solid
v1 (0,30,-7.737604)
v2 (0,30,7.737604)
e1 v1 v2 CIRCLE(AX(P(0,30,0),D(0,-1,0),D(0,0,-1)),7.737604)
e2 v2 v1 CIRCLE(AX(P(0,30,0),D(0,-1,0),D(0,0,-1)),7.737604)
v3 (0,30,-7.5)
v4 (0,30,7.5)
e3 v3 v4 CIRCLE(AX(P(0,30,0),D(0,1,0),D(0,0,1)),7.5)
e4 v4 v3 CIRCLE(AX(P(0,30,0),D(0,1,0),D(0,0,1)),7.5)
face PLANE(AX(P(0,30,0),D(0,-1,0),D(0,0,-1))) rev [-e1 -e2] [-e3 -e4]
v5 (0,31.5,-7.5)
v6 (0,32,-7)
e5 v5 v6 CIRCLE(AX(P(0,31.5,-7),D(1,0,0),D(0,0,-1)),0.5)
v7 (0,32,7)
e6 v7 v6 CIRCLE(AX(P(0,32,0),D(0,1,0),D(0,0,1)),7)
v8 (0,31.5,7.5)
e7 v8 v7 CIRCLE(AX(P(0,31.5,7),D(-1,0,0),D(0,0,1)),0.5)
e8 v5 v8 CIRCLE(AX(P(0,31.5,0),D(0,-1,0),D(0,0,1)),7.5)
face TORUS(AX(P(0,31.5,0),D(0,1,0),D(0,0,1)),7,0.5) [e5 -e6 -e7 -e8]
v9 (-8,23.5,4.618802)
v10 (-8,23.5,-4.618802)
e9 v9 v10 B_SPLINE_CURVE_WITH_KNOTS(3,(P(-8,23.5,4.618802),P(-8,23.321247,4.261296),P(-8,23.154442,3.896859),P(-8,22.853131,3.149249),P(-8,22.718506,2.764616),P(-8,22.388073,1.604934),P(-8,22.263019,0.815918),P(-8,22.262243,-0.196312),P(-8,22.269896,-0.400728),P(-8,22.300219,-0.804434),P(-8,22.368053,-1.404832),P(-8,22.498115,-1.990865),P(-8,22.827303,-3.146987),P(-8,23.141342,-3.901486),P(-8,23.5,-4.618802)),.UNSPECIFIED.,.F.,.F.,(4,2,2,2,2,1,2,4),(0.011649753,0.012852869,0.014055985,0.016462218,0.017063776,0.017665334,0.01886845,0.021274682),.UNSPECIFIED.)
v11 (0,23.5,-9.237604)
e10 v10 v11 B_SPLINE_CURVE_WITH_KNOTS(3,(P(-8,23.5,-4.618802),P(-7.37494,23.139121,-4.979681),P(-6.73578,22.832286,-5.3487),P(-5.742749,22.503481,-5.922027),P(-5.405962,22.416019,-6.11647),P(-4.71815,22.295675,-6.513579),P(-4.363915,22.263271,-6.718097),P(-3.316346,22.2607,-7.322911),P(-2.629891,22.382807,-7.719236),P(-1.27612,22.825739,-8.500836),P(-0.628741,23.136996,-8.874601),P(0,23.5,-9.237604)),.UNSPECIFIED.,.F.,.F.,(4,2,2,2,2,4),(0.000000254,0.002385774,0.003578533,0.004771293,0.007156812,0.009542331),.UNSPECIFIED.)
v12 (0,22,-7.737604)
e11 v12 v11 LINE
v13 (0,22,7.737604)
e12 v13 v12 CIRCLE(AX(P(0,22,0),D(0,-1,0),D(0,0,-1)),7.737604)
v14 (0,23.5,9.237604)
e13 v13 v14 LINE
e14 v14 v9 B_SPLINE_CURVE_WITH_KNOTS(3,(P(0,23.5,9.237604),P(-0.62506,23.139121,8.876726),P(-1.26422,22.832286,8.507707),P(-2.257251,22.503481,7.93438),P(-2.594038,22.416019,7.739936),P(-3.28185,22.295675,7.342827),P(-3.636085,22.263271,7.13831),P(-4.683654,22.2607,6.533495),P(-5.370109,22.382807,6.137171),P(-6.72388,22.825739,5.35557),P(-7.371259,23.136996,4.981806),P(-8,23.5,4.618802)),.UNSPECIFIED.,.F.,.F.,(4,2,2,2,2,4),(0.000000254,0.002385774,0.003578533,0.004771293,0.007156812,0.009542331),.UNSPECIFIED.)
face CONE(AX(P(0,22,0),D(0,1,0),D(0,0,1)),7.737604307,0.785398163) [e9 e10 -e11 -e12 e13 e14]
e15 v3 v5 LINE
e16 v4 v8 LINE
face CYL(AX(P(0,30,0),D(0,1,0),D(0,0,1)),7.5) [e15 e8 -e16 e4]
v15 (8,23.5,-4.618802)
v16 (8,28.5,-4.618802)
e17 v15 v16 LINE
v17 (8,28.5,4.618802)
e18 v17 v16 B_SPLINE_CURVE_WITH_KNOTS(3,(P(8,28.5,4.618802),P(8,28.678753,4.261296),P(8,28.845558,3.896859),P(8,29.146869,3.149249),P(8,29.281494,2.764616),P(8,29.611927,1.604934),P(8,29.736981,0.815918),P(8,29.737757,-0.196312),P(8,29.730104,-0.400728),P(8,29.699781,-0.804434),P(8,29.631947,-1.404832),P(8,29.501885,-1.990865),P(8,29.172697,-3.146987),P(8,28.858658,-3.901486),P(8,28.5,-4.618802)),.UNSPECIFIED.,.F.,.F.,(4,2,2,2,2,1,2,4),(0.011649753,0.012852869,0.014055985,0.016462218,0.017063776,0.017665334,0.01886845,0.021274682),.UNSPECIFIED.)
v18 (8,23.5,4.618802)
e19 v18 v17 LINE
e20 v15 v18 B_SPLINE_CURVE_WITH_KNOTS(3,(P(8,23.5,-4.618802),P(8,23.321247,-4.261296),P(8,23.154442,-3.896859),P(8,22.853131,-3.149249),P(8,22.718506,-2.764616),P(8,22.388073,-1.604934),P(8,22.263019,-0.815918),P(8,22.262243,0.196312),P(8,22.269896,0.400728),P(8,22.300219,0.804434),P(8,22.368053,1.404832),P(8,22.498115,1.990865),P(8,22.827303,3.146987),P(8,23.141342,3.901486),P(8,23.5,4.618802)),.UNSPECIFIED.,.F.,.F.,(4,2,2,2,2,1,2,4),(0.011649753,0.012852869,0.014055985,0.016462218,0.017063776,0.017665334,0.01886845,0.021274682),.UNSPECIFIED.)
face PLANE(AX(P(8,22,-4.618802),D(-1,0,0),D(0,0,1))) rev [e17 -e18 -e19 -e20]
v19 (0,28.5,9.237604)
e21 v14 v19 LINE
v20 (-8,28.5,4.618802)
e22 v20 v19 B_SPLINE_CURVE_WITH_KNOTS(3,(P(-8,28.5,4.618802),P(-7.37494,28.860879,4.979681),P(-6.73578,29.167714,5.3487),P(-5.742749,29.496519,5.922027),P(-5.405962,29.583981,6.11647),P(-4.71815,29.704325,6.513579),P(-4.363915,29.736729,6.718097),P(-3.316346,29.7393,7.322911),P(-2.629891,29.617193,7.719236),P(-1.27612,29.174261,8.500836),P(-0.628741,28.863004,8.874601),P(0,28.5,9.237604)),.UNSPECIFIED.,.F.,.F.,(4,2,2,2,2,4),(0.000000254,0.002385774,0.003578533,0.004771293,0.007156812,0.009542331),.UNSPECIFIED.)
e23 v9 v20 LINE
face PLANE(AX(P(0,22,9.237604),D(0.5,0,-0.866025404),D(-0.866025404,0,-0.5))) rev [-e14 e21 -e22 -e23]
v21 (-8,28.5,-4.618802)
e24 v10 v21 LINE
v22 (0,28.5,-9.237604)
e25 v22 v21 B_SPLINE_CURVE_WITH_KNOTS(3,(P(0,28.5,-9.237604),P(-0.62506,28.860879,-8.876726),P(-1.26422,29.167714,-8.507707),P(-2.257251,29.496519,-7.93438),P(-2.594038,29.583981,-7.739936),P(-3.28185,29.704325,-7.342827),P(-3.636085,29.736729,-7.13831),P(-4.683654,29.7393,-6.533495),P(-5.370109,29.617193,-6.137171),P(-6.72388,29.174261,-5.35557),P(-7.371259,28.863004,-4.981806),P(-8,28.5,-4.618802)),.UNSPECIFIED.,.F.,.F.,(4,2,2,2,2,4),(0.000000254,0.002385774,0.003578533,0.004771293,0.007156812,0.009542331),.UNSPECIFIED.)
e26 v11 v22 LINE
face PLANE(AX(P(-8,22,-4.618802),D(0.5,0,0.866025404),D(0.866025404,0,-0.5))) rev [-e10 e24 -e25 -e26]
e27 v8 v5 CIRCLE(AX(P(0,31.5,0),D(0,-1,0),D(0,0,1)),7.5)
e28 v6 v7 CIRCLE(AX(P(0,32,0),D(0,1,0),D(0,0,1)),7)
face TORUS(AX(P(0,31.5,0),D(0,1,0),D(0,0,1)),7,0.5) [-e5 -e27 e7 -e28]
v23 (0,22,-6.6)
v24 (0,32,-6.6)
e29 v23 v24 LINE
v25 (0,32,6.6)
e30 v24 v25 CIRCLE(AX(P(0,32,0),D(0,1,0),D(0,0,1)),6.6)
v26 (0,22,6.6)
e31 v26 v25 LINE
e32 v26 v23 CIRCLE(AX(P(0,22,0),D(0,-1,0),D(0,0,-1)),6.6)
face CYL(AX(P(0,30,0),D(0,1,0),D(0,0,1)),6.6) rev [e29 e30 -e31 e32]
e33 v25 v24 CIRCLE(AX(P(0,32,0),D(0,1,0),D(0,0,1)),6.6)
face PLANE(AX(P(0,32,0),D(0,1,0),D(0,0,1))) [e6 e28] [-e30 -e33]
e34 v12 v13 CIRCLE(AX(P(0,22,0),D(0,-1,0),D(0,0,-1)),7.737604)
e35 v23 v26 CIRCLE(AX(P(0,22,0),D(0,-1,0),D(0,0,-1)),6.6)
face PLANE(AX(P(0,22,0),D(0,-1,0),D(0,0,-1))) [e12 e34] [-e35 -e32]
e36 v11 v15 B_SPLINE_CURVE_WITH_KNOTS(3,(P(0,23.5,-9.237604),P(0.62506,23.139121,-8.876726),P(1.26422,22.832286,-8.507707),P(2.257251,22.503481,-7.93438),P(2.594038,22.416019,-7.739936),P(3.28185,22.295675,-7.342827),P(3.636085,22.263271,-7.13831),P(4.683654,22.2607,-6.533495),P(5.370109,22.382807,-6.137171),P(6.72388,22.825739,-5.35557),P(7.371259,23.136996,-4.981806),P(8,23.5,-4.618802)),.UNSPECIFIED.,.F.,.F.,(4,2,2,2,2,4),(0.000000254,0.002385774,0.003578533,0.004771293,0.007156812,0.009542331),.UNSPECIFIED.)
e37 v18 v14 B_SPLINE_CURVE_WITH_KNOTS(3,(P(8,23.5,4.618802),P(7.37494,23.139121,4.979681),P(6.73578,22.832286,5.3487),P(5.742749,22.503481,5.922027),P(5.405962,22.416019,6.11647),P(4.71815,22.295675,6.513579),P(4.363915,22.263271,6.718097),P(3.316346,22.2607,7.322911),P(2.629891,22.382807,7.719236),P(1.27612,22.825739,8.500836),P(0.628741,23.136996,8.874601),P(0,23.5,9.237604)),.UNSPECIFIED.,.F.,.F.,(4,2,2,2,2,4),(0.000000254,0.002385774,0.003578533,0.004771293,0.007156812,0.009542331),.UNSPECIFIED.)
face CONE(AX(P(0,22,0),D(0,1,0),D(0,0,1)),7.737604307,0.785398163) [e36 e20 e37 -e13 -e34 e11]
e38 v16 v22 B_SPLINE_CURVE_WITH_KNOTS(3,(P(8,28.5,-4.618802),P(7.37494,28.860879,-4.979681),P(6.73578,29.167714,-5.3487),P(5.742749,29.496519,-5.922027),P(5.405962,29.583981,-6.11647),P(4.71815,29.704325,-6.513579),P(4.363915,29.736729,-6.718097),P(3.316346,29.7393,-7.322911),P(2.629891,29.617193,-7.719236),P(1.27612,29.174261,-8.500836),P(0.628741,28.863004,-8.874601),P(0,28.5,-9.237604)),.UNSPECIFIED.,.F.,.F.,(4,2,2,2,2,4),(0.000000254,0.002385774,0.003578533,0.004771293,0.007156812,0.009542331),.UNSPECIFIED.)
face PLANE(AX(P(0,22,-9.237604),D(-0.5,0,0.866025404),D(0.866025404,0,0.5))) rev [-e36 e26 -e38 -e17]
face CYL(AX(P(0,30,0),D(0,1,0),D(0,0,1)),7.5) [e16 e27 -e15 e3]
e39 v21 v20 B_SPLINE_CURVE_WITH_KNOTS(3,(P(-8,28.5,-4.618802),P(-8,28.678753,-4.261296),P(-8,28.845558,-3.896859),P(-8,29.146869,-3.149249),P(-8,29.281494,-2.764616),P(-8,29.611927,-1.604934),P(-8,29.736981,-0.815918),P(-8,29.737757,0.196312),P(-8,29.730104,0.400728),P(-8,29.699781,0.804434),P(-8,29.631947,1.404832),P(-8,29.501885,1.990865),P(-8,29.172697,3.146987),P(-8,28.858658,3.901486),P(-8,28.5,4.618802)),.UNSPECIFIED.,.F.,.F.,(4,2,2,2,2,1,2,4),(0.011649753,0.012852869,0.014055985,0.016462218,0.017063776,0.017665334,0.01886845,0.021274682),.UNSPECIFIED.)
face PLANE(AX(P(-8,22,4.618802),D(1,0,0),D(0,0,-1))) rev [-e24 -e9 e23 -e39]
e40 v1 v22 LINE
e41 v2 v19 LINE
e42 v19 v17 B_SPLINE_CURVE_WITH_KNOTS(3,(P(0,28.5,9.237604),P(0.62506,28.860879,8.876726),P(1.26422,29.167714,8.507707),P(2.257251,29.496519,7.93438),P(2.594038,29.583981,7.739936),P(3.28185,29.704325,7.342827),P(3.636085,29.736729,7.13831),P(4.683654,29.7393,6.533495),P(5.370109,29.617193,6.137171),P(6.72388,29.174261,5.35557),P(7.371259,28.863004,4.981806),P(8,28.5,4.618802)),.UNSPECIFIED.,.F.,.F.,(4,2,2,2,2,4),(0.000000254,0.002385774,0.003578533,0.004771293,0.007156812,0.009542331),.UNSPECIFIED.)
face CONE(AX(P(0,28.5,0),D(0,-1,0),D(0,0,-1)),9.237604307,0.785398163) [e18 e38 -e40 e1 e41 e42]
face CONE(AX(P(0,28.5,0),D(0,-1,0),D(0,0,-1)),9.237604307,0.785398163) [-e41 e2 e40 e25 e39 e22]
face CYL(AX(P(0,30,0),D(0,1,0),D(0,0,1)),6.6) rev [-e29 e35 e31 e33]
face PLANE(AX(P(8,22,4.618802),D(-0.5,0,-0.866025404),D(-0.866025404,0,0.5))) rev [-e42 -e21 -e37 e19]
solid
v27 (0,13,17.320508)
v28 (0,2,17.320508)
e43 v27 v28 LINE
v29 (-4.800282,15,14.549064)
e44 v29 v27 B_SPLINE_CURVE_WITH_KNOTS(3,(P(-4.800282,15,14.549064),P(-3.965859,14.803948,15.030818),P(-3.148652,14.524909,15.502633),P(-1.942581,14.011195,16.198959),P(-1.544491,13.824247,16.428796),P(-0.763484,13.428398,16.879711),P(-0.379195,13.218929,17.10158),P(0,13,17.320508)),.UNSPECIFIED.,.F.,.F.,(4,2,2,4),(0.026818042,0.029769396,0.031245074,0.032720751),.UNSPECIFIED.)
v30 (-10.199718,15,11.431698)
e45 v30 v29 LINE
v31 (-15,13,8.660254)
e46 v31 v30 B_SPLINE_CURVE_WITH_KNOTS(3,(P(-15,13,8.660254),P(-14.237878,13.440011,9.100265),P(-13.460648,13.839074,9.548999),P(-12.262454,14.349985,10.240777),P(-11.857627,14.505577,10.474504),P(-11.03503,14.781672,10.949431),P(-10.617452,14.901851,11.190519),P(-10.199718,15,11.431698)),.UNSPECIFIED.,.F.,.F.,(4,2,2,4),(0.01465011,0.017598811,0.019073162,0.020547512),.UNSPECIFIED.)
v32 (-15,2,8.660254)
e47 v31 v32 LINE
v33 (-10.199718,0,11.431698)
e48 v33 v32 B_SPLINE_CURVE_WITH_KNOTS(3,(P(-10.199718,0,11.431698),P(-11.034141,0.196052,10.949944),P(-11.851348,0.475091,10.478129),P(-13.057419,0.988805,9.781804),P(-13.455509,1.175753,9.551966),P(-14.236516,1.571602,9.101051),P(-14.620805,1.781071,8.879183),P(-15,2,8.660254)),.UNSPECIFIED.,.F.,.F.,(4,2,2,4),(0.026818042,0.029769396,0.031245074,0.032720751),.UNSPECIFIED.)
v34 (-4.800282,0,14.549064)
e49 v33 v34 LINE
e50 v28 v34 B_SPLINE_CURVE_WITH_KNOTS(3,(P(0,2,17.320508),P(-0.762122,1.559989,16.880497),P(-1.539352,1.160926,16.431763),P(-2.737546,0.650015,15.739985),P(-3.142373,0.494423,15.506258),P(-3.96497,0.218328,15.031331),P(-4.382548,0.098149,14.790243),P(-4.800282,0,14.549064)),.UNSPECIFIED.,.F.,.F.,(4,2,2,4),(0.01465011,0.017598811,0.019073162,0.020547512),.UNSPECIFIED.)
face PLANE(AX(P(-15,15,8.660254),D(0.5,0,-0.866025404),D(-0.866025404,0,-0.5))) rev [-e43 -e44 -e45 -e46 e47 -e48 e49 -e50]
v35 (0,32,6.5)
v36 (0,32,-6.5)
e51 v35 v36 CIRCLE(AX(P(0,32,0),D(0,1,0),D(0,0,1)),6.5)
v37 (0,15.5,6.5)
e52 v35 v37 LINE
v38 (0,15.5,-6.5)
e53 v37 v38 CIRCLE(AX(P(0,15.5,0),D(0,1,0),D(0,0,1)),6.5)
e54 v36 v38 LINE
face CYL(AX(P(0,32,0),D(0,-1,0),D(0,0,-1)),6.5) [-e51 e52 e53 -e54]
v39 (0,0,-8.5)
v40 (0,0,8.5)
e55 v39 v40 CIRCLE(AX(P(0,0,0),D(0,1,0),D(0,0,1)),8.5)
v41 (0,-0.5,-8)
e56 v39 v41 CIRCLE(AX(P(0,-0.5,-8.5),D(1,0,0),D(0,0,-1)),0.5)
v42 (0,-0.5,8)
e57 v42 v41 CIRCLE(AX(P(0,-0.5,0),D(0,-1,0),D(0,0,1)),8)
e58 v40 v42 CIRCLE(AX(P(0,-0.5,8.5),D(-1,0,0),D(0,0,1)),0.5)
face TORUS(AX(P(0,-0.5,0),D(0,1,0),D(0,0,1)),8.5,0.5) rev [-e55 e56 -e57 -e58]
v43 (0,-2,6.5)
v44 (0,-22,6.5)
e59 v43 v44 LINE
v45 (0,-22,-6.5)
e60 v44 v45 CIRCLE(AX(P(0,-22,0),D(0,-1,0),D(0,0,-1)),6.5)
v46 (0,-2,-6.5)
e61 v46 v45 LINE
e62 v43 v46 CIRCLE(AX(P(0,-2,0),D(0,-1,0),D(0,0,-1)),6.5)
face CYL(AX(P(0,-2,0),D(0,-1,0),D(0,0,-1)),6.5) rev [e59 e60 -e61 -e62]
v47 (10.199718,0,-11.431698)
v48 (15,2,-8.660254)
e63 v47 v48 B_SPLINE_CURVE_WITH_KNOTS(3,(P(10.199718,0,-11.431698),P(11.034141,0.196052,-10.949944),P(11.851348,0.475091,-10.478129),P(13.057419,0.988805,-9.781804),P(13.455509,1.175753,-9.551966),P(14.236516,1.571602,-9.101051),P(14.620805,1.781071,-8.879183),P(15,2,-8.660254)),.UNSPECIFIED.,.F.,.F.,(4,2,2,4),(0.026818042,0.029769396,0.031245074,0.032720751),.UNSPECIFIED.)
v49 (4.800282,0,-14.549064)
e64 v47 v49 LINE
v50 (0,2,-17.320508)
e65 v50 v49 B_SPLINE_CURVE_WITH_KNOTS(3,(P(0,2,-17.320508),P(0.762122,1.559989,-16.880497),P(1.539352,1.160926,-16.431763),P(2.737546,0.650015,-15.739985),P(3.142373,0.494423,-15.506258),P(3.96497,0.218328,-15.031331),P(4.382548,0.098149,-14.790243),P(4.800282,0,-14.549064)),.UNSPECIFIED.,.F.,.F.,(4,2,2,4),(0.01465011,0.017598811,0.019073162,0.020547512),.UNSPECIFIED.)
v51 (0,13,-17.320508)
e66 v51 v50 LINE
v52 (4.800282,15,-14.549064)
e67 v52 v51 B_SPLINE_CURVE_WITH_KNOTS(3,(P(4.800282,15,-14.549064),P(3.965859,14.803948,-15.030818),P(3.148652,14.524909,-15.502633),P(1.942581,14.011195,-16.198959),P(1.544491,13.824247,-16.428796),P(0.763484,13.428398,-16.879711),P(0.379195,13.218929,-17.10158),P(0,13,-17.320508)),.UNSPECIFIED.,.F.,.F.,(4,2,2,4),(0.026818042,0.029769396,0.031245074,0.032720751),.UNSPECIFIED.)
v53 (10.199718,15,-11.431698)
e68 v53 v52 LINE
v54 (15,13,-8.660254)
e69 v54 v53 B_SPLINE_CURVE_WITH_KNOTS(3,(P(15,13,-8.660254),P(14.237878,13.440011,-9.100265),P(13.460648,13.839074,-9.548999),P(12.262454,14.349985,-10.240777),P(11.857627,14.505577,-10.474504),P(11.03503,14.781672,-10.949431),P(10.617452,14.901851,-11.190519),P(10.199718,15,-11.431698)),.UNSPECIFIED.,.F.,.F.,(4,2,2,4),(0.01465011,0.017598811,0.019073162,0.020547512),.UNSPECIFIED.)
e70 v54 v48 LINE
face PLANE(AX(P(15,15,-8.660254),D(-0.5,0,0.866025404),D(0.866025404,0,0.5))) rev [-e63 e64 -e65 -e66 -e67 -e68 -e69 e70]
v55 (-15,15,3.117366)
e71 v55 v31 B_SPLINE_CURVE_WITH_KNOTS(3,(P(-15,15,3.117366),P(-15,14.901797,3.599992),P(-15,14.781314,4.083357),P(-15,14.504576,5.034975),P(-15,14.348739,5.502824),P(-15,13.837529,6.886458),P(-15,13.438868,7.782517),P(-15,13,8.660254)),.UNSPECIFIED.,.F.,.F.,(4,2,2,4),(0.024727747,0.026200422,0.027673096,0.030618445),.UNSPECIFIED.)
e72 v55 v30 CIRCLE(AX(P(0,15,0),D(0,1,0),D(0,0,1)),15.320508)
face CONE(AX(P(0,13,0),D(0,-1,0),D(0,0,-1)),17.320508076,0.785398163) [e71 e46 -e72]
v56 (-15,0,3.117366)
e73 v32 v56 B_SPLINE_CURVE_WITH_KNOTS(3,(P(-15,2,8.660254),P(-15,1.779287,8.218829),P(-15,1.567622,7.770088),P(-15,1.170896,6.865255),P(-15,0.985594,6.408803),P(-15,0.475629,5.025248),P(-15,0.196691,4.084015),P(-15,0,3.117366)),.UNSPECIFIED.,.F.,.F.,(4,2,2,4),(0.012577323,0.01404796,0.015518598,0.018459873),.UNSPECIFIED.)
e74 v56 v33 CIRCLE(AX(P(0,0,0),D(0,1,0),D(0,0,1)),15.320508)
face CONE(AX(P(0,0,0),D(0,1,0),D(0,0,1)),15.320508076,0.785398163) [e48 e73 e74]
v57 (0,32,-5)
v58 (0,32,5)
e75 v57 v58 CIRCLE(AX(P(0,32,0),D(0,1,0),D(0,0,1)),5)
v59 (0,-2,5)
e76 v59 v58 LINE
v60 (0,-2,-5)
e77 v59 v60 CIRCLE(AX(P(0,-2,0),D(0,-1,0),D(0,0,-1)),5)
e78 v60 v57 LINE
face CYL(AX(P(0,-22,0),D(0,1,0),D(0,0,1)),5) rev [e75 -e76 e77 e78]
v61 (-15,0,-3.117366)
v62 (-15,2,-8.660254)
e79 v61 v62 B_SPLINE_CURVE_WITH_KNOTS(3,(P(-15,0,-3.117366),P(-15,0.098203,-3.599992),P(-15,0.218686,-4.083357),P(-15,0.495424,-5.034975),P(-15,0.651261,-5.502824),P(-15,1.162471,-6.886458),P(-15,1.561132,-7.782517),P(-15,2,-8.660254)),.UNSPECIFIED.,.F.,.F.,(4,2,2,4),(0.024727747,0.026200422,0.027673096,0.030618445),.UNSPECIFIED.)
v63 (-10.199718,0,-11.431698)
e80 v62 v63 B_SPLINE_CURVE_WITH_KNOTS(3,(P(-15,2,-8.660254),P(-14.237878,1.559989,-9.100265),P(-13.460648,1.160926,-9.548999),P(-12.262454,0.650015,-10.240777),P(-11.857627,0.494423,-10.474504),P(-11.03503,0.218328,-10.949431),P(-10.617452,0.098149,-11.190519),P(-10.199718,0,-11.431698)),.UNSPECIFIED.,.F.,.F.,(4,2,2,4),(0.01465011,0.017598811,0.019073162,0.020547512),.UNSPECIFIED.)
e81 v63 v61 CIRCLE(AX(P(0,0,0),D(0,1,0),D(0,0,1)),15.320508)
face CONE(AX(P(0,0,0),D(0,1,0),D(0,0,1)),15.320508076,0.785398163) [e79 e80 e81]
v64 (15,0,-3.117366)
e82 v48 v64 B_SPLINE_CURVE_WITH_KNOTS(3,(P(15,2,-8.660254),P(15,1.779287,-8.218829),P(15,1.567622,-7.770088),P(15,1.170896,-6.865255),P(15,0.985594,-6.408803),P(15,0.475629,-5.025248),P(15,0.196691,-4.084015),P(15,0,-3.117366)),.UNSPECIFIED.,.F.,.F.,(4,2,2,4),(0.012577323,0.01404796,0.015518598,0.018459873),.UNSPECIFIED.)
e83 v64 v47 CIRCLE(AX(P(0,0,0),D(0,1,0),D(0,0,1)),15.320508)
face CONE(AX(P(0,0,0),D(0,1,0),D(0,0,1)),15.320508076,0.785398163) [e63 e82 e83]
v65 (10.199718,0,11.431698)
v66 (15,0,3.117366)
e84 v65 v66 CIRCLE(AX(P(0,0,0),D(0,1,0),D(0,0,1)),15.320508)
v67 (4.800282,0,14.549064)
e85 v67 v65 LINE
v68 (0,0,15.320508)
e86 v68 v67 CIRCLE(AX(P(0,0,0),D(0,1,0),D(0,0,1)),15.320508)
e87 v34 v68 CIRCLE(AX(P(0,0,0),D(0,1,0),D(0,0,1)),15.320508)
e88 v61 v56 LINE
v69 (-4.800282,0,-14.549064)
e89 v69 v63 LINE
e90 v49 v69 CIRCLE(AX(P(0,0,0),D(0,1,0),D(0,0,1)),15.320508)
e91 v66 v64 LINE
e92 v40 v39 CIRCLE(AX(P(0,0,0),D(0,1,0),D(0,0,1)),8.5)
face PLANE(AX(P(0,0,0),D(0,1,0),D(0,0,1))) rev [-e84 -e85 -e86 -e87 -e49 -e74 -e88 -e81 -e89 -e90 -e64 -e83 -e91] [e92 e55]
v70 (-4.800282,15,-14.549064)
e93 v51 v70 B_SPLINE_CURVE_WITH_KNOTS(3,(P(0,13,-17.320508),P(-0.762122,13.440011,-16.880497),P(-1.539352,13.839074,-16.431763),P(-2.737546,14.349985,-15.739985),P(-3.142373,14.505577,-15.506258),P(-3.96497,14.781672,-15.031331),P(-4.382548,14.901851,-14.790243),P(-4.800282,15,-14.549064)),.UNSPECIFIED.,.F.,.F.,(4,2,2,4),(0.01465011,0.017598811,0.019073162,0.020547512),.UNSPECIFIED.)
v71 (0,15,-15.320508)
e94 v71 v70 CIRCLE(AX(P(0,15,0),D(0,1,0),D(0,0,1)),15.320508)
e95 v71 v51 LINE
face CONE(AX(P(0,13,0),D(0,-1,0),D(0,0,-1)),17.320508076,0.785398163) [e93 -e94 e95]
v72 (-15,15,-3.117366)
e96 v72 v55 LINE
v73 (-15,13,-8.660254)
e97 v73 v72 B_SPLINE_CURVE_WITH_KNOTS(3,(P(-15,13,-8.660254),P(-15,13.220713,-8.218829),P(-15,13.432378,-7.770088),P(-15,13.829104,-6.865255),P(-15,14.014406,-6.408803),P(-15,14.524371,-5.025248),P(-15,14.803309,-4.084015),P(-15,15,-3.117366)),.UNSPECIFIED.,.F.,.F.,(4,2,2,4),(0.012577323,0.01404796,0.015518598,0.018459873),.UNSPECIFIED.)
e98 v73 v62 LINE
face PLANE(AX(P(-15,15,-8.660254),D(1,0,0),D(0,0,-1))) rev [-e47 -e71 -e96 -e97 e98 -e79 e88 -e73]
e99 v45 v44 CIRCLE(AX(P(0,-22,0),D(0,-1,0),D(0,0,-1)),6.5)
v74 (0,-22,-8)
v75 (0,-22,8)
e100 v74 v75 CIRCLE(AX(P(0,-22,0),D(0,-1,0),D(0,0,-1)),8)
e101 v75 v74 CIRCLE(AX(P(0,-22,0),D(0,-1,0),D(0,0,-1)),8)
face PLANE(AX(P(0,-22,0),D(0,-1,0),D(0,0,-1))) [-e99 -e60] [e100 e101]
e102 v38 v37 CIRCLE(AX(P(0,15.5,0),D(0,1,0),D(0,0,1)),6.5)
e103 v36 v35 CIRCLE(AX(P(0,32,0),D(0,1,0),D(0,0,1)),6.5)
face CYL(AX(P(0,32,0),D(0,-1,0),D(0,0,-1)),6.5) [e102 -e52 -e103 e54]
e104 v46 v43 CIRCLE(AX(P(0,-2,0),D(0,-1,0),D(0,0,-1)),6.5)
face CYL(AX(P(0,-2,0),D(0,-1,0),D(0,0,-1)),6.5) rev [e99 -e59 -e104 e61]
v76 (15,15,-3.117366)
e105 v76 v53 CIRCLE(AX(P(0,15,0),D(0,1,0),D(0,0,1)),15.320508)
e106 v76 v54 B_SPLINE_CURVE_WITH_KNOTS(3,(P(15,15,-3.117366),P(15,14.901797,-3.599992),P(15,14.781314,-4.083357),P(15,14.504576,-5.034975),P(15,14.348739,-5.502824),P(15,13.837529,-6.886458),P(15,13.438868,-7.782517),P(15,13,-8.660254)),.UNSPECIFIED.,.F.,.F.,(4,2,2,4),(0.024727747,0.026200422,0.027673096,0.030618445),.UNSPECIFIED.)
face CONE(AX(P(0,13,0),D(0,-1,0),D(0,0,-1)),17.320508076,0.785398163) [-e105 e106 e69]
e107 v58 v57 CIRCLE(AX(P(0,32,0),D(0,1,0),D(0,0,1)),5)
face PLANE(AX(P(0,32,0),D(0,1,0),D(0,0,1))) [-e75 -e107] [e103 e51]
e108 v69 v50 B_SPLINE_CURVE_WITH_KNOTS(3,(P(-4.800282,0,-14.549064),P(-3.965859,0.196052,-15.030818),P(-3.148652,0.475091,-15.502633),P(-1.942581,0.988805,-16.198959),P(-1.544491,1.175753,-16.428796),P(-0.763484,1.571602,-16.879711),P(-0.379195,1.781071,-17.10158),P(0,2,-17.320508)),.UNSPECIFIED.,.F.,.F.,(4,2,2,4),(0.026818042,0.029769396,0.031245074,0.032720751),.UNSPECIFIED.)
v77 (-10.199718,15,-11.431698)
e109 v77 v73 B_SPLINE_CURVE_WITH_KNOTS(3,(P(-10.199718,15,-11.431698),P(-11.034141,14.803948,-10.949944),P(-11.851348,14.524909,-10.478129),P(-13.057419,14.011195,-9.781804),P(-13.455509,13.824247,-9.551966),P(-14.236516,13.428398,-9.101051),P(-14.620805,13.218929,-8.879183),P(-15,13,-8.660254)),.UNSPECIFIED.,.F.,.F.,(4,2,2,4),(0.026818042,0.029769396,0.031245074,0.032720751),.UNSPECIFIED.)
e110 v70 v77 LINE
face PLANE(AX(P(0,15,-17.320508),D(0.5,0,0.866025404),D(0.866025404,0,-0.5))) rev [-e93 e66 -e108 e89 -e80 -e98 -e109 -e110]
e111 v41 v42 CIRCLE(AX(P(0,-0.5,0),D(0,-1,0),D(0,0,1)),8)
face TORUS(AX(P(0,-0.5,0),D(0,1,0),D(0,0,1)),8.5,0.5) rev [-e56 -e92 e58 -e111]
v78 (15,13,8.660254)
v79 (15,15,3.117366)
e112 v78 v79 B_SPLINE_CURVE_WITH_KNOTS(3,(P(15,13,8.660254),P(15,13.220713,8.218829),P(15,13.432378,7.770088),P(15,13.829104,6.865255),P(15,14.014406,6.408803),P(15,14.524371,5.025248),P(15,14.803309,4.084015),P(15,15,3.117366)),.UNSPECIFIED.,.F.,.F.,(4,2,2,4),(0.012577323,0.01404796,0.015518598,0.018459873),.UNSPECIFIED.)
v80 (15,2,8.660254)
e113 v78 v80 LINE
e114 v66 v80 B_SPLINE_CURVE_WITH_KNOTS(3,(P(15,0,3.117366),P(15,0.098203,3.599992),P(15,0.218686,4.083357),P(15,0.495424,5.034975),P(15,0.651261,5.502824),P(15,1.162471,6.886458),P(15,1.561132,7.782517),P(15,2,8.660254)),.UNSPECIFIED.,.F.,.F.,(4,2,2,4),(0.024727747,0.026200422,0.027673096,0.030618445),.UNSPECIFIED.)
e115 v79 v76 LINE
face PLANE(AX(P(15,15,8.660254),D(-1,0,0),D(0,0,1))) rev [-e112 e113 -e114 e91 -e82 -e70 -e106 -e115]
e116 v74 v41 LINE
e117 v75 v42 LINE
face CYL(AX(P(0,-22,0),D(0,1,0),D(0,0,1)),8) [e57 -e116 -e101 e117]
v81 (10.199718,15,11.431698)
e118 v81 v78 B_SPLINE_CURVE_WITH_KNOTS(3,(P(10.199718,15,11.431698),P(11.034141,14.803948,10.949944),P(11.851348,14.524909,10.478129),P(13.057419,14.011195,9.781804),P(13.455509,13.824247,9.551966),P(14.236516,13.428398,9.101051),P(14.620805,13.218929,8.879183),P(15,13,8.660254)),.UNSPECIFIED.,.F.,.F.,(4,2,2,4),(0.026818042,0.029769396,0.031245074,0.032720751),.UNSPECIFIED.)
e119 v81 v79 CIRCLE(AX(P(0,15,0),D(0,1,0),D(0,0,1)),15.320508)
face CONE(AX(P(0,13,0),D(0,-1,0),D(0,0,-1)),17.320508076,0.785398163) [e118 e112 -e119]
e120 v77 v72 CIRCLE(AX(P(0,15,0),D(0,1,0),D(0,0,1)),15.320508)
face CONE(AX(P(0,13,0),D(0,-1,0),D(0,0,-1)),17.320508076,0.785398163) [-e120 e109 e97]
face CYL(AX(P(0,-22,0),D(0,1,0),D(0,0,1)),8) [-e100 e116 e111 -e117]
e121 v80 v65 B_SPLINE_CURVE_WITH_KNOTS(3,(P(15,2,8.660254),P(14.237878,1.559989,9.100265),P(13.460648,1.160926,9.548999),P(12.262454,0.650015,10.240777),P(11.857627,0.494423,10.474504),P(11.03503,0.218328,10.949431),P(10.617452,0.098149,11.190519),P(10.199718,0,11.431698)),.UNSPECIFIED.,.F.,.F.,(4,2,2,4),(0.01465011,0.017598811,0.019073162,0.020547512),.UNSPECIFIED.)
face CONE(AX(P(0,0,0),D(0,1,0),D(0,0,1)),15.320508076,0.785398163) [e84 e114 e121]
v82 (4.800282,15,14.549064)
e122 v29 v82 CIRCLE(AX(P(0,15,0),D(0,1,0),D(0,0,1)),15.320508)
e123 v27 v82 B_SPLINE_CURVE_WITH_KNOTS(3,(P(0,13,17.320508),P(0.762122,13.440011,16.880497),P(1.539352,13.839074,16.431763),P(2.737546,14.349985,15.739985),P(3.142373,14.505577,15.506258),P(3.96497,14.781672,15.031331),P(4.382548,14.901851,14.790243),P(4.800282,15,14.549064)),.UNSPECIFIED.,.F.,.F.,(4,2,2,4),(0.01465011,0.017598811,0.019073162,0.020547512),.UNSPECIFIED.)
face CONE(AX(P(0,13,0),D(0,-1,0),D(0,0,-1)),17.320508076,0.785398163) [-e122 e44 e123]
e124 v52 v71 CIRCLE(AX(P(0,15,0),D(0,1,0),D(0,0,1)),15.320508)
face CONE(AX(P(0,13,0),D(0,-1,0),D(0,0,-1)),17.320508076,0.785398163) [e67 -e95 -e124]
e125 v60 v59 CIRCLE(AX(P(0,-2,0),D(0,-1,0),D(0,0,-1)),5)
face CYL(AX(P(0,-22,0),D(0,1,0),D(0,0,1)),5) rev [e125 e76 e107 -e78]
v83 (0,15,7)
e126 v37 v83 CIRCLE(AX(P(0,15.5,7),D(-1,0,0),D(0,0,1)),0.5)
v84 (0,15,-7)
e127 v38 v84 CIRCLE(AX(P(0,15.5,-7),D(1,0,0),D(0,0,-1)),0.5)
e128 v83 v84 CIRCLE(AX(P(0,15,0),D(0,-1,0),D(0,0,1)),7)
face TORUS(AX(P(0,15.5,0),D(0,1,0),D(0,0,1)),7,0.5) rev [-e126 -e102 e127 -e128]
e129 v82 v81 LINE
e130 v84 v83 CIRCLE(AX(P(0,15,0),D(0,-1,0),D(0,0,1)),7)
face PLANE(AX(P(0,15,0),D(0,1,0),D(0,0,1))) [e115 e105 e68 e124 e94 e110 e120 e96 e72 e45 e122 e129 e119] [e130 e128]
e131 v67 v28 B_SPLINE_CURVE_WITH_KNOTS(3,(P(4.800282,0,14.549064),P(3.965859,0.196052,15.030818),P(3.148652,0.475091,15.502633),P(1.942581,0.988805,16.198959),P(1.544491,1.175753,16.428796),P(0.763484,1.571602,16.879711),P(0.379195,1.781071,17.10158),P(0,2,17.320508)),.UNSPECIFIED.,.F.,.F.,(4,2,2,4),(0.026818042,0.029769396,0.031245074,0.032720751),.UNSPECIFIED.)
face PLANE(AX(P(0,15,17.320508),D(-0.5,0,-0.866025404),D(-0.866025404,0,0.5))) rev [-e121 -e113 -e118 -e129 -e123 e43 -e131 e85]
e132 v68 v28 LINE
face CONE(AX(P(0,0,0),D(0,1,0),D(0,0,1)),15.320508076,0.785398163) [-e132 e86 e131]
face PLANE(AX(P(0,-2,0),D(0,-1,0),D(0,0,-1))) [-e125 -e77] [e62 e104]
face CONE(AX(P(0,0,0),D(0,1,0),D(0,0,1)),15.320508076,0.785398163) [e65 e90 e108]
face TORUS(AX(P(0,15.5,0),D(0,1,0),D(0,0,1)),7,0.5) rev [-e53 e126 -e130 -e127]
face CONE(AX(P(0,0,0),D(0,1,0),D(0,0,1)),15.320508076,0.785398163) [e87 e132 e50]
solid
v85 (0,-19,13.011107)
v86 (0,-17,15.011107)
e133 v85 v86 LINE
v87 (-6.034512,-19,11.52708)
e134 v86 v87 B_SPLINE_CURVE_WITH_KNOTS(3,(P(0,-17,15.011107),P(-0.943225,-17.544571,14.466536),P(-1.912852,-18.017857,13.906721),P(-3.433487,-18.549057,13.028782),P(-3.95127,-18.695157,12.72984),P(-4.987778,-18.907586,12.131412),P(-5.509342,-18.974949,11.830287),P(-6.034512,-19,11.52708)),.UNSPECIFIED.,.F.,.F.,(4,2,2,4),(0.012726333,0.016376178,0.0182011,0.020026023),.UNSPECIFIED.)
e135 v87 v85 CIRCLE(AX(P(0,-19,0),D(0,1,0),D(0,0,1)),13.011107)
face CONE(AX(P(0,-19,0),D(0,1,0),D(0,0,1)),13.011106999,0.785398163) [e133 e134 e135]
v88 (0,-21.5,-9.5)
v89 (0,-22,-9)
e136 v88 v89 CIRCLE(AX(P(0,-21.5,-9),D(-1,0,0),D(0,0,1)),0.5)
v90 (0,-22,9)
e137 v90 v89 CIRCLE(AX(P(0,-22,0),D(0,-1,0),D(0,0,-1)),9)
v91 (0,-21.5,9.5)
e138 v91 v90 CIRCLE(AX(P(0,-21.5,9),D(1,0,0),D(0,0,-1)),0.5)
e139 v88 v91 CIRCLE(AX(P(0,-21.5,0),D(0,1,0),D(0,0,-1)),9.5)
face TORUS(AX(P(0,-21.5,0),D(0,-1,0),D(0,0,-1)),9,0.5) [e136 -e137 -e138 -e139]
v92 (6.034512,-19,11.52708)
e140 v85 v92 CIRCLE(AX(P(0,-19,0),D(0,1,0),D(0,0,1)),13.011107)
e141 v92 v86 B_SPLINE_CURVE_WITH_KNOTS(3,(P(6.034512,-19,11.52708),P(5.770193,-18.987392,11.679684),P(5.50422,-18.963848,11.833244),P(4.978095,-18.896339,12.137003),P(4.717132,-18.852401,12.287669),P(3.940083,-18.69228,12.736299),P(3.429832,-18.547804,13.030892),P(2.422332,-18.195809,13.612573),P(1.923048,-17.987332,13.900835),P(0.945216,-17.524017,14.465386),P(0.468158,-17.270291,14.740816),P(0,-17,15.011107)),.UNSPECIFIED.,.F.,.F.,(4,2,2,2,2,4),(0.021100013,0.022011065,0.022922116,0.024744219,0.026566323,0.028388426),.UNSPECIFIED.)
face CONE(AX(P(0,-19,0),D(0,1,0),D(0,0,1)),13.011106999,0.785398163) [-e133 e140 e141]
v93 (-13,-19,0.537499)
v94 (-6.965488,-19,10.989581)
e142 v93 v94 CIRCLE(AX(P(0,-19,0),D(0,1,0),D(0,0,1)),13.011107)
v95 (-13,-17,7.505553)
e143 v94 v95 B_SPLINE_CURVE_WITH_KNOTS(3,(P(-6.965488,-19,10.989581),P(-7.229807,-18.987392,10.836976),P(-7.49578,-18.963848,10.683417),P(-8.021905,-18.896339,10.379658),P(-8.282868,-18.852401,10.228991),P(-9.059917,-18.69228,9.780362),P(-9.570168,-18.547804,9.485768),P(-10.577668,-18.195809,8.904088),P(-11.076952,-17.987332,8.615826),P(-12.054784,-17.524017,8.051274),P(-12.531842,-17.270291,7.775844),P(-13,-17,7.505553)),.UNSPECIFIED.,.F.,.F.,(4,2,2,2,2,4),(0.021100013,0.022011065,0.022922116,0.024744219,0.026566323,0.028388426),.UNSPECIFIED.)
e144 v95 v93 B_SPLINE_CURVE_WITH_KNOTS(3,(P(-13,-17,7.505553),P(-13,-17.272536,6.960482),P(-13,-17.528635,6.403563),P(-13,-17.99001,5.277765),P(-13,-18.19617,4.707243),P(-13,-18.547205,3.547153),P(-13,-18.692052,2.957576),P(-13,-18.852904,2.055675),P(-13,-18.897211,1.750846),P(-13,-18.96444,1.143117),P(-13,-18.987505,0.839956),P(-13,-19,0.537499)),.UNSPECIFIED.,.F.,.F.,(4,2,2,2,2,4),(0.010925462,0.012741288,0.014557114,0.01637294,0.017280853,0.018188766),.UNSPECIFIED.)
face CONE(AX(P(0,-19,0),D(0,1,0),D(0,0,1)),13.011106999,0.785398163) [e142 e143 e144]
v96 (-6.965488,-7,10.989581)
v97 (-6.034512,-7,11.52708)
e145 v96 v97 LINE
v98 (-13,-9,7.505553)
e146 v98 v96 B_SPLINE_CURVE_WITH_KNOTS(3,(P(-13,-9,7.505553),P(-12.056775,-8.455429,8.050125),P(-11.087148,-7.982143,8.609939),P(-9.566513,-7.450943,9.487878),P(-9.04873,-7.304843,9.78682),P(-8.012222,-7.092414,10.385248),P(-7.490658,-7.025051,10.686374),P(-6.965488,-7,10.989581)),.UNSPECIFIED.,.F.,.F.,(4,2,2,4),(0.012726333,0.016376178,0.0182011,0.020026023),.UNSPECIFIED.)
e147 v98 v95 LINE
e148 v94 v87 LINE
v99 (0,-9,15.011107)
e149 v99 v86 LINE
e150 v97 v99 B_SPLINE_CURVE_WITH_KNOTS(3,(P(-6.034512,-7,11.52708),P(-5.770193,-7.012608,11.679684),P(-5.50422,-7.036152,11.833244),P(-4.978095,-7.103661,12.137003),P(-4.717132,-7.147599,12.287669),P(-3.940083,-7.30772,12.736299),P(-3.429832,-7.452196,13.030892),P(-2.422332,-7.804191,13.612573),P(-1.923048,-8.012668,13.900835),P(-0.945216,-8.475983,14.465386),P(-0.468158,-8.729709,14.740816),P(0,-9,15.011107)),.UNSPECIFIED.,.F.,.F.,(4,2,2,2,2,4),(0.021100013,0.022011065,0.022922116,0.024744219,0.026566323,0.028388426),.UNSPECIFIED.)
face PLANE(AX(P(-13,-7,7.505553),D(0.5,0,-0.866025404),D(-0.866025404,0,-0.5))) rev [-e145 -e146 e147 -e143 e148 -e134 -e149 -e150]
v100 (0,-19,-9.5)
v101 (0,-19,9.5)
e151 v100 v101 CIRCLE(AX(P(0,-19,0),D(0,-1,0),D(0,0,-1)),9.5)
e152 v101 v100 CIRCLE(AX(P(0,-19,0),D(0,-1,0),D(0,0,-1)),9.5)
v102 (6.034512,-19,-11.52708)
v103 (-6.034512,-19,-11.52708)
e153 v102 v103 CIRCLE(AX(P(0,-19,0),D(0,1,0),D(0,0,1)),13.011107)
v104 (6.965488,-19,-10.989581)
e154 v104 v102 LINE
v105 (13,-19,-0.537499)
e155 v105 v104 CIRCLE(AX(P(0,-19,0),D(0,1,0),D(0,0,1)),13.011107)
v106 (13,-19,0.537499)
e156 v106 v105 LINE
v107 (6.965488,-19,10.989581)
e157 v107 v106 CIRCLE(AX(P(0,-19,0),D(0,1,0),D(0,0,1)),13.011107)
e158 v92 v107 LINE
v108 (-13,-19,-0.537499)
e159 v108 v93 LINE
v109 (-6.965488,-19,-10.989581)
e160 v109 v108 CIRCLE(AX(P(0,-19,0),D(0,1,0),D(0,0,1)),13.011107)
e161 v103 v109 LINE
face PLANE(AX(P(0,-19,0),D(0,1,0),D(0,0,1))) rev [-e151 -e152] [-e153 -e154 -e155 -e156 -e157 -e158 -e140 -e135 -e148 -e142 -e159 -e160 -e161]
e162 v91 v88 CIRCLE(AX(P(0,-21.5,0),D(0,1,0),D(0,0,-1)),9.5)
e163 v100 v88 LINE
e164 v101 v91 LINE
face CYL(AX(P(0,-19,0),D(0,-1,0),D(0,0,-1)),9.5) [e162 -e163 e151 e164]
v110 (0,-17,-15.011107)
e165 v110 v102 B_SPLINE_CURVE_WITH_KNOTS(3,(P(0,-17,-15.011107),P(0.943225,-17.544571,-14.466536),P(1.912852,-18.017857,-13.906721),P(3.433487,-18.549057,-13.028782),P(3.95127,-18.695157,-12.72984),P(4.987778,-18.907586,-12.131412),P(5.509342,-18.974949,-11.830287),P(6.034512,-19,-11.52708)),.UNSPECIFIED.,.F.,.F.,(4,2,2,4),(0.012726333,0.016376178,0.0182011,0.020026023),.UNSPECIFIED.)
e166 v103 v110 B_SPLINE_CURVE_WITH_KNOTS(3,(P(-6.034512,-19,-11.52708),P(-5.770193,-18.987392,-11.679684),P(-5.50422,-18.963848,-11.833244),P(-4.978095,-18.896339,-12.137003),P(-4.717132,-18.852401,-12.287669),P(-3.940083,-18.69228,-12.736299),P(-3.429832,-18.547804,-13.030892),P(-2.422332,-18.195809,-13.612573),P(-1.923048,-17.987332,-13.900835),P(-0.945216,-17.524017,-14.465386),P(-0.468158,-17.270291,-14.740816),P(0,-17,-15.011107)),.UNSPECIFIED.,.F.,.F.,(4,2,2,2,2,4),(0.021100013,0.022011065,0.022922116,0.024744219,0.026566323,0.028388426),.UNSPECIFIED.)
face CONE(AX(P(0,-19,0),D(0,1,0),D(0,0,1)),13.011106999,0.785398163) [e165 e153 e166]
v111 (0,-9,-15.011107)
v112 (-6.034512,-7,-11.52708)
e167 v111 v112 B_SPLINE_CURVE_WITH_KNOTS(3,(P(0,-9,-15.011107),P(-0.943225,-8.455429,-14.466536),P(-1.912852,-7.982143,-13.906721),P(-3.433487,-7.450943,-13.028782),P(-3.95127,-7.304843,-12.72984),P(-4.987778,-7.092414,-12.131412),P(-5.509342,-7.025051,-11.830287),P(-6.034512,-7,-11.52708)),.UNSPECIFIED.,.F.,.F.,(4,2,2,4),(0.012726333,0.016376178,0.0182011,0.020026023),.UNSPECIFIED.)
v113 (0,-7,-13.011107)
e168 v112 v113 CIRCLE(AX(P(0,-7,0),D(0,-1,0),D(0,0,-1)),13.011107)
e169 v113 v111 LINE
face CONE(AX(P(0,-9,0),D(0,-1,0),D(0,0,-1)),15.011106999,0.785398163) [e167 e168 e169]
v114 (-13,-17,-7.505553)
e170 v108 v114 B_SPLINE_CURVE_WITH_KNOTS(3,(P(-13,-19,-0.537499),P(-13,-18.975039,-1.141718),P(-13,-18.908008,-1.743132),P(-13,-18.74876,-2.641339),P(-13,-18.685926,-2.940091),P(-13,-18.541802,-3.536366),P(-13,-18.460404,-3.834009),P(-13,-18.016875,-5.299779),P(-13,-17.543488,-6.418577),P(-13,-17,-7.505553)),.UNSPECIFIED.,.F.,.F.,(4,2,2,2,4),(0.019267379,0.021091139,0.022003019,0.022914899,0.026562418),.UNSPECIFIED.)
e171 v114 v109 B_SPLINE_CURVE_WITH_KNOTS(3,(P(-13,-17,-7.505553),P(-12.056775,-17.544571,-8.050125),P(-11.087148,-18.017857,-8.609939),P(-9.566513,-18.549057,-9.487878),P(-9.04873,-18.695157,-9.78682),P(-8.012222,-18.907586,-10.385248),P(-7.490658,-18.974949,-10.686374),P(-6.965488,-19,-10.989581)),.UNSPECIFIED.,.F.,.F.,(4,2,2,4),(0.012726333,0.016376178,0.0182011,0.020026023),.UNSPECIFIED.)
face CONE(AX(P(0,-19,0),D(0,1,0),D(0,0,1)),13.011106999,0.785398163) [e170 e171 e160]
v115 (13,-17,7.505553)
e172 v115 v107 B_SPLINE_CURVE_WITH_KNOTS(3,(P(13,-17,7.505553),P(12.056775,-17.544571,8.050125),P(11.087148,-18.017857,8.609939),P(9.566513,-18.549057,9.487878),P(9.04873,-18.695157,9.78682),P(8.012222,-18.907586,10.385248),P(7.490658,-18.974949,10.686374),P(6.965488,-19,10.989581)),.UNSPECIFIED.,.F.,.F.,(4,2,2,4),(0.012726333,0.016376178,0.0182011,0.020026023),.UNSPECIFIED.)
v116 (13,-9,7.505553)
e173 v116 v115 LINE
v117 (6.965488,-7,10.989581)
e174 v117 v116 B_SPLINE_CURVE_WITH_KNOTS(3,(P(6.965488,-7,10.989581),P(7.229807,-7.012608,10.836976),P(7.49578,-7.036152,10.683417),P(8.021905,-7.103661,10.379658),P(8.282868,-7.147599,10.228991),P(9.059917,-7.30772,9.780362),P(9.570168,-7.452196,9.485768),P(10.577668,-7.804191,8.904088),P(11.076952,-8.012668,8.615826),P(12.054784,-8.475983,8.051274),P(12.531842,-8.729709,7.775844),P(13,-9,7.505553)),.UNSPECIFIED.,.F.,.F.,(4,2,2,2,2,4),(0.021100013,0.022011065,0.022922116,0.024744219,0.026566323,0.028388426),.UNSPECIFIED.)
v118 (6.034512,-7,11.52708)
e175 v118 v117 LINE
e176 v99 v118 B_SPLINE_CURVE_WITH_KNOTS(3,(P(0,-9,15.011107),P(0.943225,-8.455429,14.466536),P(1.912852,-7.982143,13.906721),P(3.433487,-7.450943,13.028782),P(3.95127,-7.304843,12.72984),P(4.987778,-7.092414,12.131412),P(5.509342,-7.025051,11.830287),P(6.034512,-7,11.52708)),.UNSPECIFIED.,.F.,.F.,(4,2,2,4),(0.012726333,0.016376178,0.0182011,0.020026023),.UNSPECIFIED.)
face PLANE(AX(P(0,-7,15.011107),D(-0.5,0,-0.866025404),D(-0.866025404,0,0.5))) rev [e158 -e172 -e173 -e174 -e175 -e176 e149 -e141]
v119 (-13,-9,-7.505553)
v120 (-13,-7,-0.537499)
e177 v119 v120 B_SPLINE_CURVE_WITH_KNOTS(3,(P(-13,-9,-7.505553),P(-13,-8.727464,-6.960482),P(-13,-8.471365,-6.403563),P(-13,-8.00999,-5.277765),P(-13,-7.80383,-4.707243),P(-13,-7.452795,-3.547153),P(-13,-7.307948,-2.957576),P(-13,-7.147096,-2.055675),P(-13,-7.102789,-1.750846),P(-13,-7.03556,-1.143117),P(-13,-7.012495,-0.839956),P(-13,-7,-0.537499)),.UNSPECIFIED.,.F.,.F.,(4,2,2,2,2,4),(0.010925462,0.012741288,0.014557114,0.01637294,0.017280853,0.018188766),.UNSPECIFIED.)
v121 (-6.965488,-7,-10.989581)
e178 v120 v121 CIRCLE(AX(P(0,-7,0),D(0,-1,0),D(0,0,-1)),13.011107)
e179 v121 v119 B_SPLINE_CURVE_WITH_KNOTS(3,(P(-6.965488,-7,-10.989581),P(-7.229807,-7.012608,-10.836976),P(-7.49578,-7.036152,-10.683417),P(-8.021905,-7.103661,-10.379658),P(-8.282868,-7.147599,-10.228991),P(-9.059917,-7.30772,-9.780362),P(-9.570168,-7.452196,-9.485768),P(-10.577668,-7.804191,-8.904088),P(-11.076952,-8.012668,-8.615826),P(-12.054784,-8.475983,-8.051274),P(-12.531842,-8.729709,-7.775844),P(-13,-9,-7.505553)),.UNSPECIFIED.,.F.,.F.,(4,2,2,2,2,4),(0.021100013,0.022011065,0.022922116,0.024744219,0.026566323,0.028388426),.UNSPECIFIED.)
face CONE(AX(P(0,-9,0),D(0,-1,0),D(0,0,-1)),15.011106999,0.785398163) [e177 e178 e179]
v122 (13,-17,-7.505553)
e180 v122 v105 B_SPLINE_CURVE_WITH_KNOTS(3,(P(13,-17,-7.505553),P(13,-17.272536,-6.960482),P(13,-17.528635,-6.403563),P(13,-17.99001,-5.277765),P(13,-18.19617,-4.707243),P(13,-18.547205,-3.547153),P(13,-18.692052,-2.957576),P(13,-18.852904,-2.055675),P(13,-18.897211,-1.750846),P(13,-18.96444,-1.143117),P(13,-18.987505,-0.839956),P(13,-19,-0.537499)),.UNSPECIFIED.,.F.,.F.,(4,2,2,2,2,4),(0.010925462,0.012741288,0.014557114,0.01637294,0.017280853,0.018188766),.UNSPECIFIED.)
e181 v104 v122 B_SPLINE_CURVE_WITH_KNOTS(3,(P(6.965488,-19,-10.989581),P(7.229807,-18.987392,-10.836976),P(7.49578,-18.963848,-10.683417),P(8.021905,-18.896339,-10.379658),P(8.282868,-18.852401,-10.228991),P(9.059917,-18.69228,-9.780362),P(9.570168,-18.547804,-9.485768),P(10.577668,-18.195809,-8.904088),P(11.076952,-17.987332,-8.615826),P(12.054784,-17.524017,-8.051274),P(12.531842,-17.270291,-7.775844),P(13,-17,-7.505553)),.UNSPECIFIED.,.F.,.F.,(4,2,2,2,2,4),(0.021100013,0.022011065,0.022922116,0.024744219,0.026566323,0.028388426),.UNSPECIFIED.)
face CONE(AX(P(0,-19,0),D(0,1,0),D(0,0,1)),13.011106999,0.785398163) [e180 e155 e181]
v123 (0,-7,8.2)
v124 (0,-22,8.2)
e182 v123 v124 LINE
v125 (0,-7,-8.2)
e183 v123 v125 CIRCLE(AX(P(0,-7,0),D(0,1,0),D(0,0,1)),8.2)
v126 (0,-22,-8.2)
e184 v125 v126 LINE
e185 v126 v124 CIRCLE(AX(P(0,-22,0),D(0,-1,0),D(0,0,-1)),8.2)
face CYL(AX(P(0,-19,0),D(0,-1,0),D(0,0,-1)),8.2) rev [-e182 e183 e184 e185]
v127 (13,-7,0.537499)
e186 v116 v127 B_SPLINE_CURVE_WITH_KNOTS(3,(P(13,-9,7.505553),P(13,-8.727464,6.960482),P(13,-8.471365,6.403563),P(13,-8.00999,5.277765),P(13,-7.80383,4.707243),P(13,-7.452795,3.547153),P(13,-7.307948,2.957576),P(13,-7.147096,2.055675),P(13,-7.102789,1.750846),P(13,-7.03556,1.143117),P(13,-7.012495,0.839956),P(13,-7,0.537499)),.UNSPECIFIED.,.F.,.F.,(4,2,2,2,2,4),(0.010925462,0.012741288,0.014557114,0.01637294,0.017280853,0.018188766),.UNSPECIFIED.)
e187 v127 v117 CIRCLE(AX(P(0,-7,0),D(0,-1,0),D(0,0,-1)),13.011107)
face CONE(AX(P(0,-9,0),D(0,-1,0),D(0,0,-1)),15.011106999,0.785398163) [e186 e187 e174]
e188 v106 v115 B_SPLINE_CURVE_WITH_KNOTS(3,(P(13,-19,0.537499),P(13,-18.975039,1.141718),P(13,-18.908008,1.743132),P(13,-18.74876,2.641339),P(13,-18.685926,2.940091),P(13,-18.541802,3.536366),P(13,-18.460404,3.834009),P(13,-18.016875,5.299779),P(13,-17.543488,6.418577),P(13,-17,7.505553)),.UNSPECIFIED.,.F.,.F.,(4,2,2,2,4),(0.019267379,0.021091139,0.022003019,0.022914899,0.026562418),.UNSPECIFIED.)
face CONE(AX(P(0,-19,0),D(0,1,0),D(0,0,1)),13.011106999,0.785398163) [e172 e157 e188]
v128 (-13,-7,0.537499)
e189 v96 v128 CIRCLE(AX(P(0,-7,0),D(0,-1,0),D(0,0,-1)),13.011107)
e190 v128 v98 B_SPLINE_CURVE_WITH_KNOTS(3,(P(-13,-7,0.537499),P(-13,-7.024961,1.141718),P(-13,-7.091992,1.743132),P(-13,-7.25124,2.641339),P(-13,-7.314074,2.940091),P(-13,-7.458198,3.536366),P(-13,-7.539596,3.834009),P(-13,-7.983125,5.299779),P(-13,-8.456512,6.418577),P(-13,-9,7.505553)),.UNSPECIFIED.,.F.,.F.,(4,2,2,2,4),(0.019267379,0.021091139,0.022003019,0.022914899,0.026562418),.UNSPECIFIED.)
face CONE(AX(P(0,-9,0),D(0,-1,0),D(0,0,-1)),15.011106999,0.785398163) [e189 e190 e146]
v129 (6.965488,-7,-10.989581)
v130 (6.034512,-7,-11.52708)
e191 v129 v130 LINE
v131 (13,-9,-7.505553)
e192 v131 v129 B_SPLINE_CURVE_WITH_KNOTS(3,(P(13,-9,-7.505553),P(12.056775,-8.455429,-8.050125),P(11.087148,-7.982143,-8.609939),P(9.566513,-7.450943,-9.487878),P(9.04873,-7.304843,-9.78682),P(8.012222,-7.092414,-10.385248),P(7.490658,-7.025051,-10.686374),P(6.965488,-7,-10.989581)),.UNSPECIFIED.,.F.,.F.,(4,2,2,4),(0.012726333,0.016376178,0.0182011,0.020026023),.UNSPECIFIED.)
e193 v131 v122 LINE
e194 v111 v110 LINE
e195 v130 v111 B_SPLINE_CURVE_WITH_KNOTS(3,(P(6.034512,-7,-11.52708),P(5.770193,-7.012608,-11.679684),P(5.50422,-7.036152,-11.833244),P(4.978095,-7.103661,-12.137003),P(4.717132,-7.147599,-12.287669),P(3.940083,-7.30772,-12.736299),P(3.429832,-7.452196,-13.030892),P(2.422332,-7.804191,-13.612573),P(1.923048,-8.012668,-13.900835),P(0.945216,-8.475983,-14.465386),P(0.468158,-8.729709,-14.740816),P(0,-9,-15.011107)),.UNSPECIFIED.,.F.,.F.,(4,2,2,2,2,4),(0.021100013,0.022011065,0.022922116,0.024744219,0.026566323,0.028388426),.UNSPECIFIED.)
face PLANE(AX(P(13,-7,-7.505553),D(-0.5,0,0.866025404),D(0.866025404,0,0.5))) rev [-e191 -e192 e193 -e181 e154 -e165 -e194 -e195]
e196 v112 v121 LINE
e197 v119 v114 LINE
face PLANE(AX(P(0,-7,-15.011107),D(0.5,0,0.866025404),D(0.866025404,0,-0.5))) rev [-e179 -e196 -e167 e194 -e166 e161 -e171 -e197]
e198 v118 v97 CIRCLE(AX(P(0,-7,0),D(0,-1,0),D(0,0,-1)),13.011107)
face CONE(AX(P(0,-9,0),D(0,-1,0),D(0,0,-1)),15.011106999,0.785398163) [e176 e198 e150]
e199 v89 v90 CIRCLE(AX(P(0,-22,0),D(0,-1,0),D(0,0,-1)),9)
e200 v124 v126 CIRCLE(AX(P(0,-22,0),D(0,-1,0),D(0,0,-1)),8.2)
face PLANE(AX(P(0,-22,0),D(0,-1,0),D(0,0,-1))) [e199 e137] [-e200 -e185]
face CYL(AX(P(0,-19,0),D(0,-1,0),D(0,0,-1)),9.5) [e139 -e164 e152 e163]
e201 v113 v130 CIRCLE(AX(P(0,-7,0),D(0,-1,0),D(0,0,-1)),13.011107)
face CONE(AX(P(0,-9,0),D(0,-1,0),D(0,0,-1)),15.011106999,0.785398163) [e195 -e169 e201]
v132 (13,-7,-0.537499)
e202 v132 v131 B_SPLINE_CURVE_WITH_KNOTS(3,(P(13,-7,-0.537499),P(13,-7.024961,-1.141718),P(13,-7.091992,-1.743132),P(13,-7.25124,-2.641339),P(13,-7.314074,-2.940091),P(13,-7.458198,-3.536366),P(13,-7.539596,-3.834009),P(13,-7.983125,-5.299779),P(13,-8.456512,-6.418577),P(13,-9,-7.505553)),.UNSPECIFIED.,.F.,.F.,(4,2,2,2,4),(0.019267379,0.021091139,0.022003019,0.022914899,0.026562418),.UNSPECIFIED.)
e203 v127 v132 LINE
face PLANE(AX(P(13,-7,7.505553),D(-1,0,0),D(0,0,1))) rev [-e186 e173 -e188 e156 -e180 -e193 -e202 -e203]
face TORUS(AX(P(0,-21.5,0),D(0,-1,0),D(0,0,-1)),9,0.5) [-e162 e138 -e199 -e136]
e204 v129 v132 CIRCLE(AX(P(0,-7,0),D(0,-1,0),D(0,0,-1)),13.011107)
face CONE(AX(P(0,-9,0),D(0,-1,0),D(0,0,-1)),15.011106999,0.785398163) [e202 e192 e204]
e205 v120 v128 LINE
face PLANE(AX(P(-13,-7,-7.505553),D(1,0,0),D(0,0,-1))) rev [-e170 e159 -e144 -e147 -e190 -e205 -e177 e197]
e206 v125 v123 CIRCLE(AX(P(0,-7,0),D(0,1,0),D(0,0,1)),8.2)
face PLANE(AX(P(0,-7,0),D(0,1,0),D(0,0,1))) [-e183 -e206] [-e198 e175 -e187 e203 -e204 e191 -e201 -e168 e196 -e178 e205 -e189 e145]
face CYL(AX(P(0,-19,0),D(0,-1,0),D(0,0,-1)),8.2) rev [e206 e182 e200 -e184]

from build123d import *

# Parameters (mm, degrees)
BOSS_EXTRUDE1_DEPTH = 15
SKETCH2_R           = 6.5
BOSS_EXTRUDE2_DEPTH = 17
SKETCH3_R           = 8
BOSS_EXTRUDE3_DEPTH = 22
SKETCH4_R           = 6.5
CUT_EXTRUDE1_DEPTH  = 20
SKETCH5_R           = 5
CUT_EXTRUDE2_DEPTH  = 59.660037504
SKETCH6_R           = 7.5
SKETCH6_R_2         = 6.6
BOSS_EXTRUDE4_DEPTH = 2
SKETCH7_R           = 6.6
BOSS_EXTRUDE5_DEPTH = 8
SKETCH11_R          = 9.5
SKETCH11_R_2        = 8.2
BOSS_EXTRUDE6_DEPTH = 3
SKETCH12_R          = 8.2
BOSS_EXTRUDE7_DEPTH = 12
FILLET1_R           = 0.5
FILLET2_R           = 0.5
FILLET3_R           = 0.5


with BuildPart() as part:
    # Sketch1 → Boss-Extrude1 (new body)
    with BuildSketch(Plane(origin=(0, 0, 0), x_dir=(1, 0, 0), z_dir=(0, 1, 0))):
        Polygon((0, -17.320508076), (15, -8.660254038), (15, 8.660254038), (0, 17.320508076), (-15, 8.660254038), (-15, -8.660254038), align=None)
    extrude(amount=BOSS_EXTRUDE1_DEPTH)

    # Sketch2 → Boss-Extrude2 (add)
    with BuildSketch(Plane(origin=(0, 15, 0), x_dir=(1, 0, 0), z_dir=(0, 1, 0))):
        with Locations(Location((0, 0, 0), (0, 0, 270))):
            Circle(SKETCH2_R)
    extrude(amount=BOSS_EXTRUDE2_DEPTH)

    # Sketch3 → Boss-Extrude3 (add)
    with BuildSketch(Plane.XZ):
        with Locations(Location((0, 0, 0), (0, 0, 270))):
            Circle(SKETCH3_R)
    extrude(amount=BOSS_EXTRUDE3_DEPTH)

    # Sketch4 → Cut-Extrude1 (cut)
    with BuildSketch(Plane.XZ.offset(22)):
        with Locations(Location((0, 0, 0), (0, 0, 90))):
            Circle(SKETCH4_R)
    extrude(amount=-CUT_EXTRUDE1_DEPTH, mode=Mode.SUBTRACT)

    # Sketch5 → Cut-Extrude2 (cut, through all)
    with BuildSketch(Plane(origin=(0, 32, 0), x_dir=(1, 0, 0), z_dir=(0, 1, 0))):
        with Locations(Location((0, 0, 0), (0, 0, 270))):
            Circle(SKETCH5_R)
    extrude(amount=-CUT_EXTRUDE2_DEPTH, mode=Mode.SUBTRACT)


with BuildPart() as body_2:
    # Sketch6 → Boss-Extrude4 (new body)
    with BuildSketch(Plane(origin=(0, 32, 0), x_dir=(1, 0, 0), z_dir=(0, 1, 0))):
        with Locations(Location((0, 0, 0), (0, 0, 270))):
            Circle(SKETCH6_R)
        with Locations(Location((0, 0, 0), (0, 0, 270))):
            Circle(SKETCH6_R_2, mode=Mode.SUBTRACT)
    extrude(amount=-BOSS_EXTRUDE4_DEPTH)

    # Sketch7 → Boss-Extrude5 (add)
    with BuildSketch(Plane.XZ.offset(-30)):
        Polygon((0, 9.237604307), (-8, 4.618802154), (-8, -4.618802154), (0, -9.237604307), (8, -4.618802154), (8, 4.618802154), align=None)
        with Locations(Location((0, 0, 0), (0, 0, 90))):
            Circle(SKETCH7_R, mode=Mode.SUBTRACT)
    extrude(amount=BOSS_EXTRUDE5_DEPTH)


with BuildPart() as body_3:
    # Sketch11 → Boss-Extrude6 (new body)
    with BuildSketch(Plane.XZ.offset(22)):
        with Locations(Location((0, 0, 0), (0, 0, 270))):
            Circle(SKETCH11_R)
        with Locations(Location((0, 0, 0), (0, 0, 270))):
            Circle(SKETCH11_R_2, mode=Mode.SUBTRACT)
    extrude(amount=-BOSS_EXTRUDE6_DEPTH)

    # Sketch12 → Boss-Extrude7 (add)
    with BuildSketch(Plane(origin=(0, -19, 0), x_dir=(1, 0, 0), z_dir=(0, 1, 0))):
        Polygon((0, 15.011106999), (-13, 7.505553499), (-13, -7.505553499), (0, -15.011106999), (13, -7.505553499), (13, 7.505553499), align=None)
        with Locations(Location((0, 0, 0), (0, 0, 90))):
            Circle(SKETCH12_R, mode=Mode.SUBTRACT)
    extrude(amount=BOSS_EXTRUDE7_DEPTH)


with BuildPart() as cut_revolve2_tool:
    # Sketch9 → Cut-Revolve2 (revolve)
    with BuildSketch(Plane(origin=(0, 0, 0), x_dir=(0, 0, -1), z_dir=(1, 0, 0))):
        Polygon((-7.737604307, 30), (-9.237604307, 28.5), (-9.237604307, 30), align=None)
        Polygon((-9.237604307, 22), (-7.737604307, 22), (-9.237604307, 23.5), align=None)
        Polygon((-17.320508076, 15), (-17.320508076, 13), (-15.320508076, 15), align=None)
        Polygon((-15.320508076, 0), (-17.320508076, 0), (-17.320508076, 2), align=None)
        Polygon((-15.011106999, -7), (-15.011106999, -9), (-13.011106999, -7), align=None)
        Polygon((-13.011106999, -19), (-15.011106999, -19), (-15.011106999, -17), align=None)
    revolve(axis=Axis((0, 32, 0), (0, 1, 0)))


with BuildPart() as part_1:
    add(part.part)

    # Cut-Revolve2: cut by cut_revolve2_tool
    add(cut_revolve2_tool.part, mode=Mode.SUBTRACT)

    # Fillet2
    fillet2_edges = [part_1.edges().sort_by_distance(p)[0] for p in [
        (0, 15, -6.5),
        (0, 0, 8),
    ]]
    fillet(fillet2_edges, radius=FILLET2_R)


with BuildPart() as body_2_1:
    add(body_2.part)

    # Cut-Revolve2: cut by cut_revolve2_tool
    add(cut_revolve2_tool.part, mode=Mode.SUBTRACT)

    # Fillet1
    fillet1_edges = [body_2_1.edges().sort_by_distance(p)[0] for p in [
        (0, 32, -7.5),
    ]]
    fillet(fillet1_edges, radius=FILLET1_R)


with BuildPart() as body_3_1:
    add(body_3.part)

    # Cut-Revolve2: cut by cut_revolve2_tool
    add(cut_revolve2_tool.part, mode=Mode.SUBTRACT)

    # Fillet3
    fillet3_edges = [body_3_1.edges().sort_by_distance(p)[0] for p in [
        (0, -22, 9.5),
    ]]
    fillet(fillet3_edges, radius=FILLET3_R)


solid = Compound([part_1.part, body_2_1.part, body_3_1.part])
